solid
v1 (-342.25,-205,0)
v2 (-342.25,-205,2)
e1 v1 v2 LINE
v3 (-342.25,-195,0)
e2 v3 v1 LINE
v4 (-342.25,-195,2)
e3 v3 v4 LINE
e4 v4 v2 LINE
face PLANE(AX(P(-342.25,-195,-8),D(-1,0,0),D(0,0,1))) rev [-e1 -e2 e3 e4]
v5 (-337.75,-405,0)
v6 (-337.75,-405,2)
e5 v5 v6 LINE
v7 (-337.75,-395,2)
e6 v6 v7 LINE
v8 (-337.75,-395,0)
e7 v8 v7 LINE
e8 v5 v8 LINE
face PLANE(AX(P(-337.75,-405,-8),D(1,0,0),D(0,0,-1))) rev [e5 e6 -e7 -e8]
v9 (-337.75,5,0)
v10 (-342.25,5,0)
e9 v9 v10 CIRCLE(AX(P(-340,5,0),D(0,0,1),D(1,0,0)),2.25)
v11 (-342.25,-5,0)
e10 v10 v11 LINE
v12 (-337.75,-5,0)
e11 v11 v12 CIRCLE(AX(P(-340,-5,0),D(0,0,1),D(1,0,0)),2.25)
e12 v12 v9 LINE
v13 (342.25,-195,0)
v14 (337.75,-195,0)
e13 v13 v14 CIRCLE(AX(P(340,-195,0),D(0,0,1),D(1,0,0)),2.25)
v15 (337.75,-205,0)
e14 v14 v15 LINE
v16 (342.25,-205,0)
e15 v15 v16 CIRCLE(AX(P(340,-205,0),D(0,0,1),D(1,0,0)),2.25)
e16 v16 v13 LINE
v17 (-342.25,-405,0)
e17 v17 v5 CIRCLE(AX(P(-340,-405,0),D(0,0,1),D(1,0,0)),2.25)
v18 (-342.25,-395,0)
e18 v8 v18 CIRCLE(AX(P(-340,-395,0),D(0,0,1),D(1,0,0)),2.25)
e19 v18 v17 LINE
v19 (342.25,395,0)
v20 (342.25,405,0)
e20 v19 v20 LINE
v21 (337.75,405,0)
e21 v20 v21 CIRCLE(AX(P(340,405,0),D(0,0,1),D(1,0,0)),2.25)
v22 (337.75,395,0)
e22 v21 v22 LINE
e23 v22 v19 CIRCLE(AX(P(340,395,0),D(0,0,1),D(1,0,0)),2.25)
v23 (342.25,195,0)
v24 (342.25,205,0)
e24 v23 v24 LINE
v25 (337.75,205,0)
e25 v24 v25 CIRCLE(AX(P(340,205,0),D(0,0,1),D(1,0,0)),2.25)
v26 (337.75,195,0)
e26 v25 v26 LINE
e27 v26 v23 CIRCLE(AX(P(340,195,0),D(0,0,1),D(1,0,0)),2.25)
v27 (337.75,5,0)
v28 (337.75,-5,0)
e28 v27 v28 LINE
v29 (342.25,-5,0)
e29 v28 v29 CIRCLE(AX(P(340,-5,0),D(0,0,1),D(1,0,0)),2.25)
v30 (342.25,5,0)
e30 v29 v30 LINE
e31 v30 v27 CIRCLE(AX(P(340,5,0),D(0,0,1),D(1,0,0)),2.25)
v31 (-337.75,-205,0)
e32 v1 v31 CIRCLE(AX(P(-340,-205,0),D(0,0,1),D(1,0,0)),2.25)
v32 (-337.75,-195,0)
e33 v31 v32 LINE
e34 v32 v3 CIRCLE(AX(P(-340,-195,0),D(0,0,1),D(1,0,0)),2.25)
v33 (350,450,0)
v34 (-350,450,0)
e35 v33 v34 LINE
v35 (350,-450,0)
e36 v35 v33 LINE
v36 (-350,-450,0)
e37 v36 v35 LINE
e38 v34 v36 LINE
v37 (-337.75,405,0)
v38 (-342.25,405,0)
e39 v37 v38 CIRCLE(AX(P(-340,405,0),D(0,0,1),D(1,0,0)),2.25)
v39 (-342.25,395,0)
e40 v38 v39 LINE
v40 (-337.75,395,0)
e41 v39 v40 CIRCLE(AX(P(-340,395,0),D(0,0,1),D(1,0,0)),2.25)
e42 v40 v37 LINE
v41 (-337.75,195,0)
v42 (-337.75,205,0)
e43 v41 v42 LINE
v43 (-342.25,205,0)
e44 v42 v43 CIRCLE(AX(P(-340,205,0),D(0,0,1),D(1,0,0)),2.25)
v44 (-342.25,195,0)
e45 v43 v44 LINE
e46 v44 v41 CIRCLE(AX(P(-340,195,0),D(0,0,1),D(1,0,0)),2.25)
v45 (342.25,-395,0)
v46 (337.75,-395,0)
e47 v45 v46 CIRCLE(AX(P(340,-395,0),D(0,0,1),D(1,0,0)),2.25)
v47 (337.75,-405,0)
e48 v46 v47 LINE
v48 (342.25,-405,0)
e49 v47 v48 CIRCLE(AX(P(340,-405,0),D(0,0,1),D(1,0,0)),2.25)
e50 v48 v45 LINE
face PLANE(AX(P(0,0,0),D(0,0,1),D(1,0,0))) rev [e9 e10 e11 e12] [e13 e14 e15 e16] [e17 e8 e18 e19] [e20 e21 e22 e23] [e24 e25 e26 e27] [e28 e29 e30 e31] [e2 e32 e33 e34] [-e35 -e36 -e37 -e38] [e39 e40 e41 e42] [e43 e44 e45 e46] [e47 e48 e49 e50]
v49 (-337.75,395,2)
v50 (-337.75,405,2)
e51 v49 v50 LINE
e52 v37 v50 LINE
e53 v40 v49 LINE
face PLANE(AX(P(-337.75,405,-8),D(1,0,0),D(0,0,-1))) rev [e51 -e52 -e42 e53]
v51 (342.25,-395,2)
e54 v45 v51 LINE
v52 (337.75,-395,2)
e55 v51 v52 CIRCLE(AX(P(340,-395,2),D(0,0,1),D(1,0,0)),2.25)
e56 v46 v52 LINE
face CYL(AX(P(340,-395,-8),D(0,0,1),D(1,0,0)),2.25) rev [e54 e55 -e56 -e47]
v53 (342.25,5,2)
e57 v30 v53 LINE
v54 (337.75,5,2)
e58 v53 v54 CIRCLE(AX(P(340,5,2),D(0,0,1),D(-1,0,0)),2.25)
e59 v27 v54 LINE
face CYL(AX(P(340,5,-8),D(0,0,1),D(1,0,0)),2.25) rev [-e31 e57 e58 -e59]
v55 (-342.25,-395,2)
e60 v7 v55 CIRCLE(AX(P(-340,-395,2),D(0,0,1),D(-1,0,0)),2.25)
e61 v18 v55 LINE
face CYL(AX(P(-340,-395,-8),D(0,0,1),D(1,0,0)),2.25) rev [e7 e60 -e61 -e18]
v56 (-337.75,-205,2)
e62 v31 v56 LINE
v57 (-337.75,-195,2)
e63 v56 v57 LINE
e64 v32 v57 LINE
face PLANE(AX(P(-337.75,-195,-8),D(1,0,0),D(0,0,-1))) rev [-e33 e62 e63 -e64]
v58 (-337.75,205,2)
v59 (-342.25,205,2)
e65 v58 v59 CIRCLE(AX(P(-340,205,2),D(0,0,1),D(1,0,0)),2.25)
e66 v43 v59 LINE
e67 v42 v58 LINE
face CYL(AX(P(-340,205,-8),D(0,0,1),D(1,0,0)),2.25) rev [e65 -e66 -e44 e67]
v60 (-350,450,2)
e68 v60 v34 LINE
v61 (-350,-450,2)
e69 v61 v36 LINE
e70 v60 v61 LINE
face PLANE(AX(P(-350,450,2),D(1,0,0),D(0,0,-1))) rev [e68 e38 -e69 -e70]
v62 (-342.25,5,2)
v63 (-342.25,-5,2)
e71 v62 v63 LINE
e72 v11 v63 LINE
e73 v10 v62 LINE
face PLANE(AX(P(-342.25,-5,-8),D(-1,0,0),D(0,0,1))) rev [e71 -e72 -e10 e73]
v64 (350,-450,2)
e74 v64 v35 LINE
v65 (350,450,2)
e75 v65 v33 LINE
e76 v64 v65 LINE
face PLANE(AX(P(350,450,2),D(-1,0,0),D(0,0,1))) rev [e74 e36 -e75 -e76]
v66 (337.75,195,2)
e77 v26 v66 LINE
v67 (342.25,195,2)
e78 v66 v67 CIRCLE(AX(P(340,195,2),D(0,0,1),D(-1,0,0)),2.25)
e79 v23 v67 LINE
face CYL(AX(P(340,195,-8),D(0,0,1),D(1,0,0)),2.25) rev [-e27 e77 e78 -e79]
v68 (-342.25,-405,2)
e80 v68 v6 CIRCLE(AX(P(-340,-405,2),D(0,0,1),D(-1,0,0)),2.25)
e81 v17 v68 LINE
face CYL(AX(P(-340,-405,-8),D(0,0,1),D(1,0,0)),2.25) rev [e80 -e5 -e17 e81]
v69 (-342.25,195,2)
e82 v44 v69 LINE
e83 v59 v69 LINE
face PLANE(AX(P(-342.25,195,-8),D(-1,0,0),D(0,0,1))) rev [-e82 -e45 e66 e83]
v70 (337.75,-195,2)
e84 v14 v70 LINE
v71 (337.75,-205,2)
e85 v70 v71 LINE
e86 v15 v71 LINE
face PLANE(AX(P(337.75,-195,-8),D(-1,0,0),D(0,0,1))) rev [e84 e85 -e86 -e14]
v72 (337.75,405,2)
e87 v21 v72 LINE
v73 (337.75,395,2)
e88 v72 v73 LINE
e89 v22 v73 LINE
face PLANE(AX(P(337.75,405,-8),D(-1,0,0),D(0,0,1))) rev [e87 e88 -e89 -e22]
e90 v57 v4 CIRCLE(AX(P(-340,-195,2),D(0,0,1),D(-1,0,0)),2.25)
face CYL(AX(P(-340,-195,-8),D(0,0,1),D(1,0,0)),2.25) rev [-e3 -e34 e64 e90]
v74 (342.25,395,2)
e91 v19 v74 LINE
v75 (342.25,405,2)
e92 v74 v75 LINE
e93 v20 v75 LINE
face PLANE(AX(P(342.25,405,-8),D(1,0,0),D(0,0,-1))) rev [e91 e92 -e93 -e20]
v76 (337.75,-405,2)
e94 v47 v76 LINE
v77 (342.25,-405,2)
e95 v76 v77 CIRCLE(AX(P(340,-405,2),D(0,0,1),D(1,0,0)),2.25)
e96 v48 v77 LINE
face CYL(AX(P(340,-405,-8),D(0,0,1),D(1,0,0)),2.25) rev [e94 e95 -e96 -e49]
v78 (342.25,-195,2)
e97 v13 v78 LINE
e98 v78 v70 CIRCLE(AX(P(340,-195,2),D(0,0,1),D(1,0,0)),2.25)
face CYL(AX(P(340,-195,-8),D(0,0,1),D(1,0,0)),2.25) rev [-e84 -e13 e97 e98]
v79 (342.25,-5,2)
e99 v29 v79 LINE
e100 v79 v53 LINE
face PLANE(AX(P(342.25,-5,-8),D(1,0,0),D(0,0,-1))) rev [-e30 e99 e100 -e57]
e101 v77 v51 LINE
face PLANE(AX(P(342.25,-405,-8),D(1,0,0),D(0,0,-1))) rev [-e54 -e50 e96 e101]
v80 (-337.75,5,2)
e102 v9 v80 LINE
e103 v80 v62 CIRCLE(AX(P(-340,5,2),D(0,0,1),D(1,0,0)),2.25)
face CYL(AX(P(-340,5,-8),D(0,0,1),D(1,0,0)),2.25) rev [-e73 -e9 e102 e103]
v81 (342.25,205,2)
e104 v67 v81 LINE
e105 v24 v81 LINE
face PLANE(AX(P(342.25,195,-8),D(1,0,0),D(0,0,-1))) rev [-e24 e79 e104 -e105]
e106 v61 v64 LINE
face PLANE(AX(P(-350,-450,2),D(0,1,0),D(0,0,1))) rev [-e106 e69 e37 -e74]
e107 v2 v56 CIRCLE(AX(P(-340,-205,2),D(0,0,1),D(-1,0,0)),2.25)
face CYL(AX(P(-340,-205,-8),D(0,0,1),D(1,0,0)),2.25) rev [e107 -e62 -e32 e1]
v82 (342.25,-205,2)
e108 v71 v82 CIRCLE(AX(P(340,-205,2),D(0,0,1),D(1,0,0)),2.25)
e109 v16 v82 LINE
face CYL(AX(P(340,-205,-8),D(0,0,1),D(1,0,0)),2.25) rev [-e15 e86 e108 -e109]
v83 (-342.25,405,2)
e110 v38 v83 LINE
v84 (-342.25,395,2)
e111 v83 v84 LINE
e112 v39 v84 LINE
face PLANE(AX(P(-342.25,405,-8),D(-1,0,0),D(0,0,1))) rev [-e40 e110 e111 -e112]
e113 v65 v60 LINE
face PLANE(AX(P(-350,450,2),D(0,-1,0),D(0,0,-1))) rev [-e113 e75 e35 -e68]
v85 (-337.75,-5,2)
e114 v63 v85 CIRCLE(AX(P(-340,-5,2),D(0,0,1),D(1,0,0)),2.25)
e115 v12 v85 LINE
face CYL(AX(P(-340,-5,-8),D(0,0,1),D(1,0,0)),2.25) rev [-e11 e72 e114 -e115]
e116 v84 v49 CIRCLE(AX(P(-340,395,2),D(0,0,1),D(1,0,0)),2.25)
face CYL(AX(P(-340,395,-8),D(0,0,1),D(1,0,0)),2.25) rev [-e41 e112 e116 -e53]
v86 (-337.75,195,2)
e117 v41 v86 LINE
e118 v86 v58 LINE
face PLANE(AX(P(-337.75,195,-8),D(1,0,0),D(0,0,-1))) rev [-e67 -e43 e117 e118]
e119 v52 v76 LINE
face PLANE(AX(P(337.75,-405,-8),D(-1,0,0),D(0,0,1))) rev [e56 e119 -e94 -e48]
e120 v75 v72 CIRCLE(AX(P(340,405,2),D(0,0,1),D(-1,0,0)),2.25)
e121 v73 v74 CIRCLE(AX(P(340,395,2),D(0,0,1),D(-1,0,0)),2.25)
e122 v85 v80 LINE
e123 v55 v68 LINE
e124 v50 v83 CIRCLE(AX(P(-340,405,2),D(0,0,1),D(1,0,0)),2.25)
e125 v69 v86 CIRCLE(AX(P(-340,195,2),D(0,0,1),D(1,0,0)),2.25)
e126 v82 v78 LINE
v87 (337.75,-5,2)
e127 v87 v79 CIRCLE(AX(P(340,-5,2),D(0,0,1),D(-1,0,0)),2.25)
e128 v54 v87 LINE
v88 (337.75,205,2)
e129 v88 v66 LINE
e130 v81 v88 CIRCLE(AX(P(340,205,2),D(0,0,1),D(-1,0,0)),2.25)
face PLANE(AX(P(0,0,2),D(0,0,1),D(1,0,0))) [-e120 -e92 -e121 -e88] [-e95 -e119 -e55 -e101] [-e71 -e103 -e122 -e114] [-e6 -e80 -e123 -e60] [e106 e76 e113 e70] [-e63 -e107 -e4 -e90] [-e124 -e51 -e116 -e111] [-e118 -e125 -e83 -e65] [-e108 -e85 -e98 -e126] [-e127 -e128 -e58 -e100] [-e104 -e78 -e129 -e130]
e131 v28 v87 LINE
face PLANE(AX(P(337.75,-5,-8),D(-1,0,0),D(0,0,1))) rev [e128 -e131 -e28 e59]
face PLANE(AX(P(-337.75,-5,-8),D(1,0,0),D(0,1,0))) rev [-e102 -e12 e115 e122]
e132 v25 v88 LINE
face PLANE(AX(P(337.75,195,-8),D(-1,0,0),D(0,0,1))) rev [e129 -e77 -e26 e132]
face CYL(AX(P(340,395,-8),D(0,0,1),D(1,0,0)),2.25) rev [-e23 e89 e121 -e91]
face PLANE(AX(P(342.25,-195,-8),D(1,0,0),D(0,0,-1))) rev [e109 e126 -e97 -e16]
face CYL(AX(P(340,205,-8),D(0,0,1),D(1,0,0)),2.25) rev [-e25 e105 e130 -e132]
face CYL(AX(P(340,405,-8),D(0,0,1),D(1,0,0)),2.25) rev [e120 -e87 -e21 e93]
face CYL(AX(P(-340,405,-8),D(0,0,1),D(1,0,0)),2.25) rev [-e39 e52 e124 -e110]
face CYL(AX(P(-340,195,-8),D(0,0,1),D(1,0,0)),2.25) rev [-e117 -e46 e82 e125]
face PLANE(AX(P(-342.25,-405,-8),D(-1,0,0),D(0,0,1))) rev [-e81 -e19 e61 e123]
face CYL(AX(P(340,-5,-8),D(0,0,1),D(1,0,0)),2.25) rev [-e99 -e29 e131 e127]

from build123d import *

# Parameters (mm, degrees)
SKETCH_1_W          = 700
SKETCH_1_H          = 900
EXTRUDE_1_DEPTH     = 2
CUT_EXTRUDE_1_DEPTH = 10


with BuildPart() as part:
    # 草图1 → 凸台-拉伸1 (new body)
    with BuildSketch(Plane.XY):
        Rectangle(SKETCH_1_W, SKETCH_1_H)
    extrude(amount=EXTRUDE_1_DEPTH)

    # 草图2 → 切除-拉伸1 (cut)
    with BuildSketch(Plane.XY.offset(2)):
        with BuildLine():
            Line((-337.75, 405), (-337.75, 395))
            ThreePointArc((-337.75, 395), (-340, 392.75), (-342.25, 395))
            Line((-342.25, 395), (-342.25, 405))
            ThreePointArc((-342.25, 405), (-340, 407.25), (-337.75, 405))
        make_face()
        with BuildLine():
            Line((337.75, 405), (337.75, 395))
            ThreePointArc((337.75, 395), (340, 392.75), (342.25, 395))
            Line((342.25, 395), (342.25, 405))
            ThreePointArc((342.25, 405), (340, 407.25), (337.75, 405))
        make_face()
        with BuildLine():
            Line((-342.25, 195), (-342.25, 205))
            ThreePointArc((-342.25, 205), (-340, 207.25), (-337.75, 205))
            Line((-337.75, 205), (-337.75, 195))
            ThreePointArc((-337.75, 195), (-340, 192.75), (-342.25, 195))
        make_face()
        with BuildLine():
            Line((-342.25, -5), (-342.25, 5))
            ThreePointArc((-342.25, 5), (-340, 7.25), (-337.75, 5))
            Line((-337.75, 5), (-337.75, -5))
            ThreePointArc((-337.75, -5), (-340, -7.25), (-342.25, -5))
        make_face()
        with BuildLine():
            Line((342.25, 195), (342.25, 205))
            ThreePointArc((342.25, 205), (340, 207.25), (337.75, 205))
            Line((337.75, 205), (337.75, 195))
            ThreePointArc((337.75, 195), (340, 192.75), (342.25, 195))
        make_face()
        with BuildLine():
            Line((342.25, -5), (342.25, 5))
            ThreePointArc((342.25, 5), (340, 7.25), (337.75, 5))
            Line((337.75, 5), (337.75, -5))
            ThreePointArc((337.75, -5), (340, -7.25), (342.25, -5))
        make_face()
        with BuildLine():
            Line((-342.25, 605), (-342.25, 595))
            ThreePointArc((-342.25, 595), (-340, 592.75), (-337.75, 595))
            Line((-337.75, 595), (-337.75, 605))
            ThreePointArc((-337.75, 605), (-340, 607.25), (-342.25, 605))
        make_face()
        with BuildLine():
            Line((342.25, 605), (342.25, 595))
            ThreePointArc((342.25, 595), (340, 592.75), (337.75, 595))
            Line((337.75, 595), (337.75, 605))
            ThreePointArc((337.75, 605), (340, 607.25), (342.25, 605))
        make_face()
        with BuildLine():
            Line((342.25, -195), (342.25, -205))
            ThreePointArc((342.25, -205), (340, -207.25), (337.75, -205))
            Line((337.75, -205), (337.75, -195))
            ThreePointArc((337.75, -195), (340, -192.75), (342.25, -195))
        make_face()
        with BuildLine():
            Line((-342.25, -195), (-342.25, -205))
            ThreePointArc((-342.25, -205), (-340, -207.25), (-337.75, -205))
            Line((-337.75, -205), (-337.75, -195))
            ThreePointArc((-337.75, -195), (-340, -192.75), (-342.25, -195))
        make_face()
        with BuildLine():
            Line((337.75, -405), (337.75, -395))
            ThreePointArc((337.75, -395), (340, -392.75), (342.25, -395))
            Line((342.25, -395), (342.25, -405))
            ThreePointArc((342.25, -405), (340, -407.25), (337.75, -405))
        make_face()
        with BuildLine():
            Line((-337.75, -405), (-337.75, -395))
            ThreePointArc((-337.75, -395), (-340, -392.75), (-342.25, -395))
            Line((-342.25, -395), (-342.25, -405))
            ThreePointArc((-342.25, -405), (-340, -407.25), (-337.75, -405))
        make_face()
    extrude(amount=-CUT_EXTRUDE_1_DEPTH, mode=Mode.SUBTRACT)


solid = part.part
